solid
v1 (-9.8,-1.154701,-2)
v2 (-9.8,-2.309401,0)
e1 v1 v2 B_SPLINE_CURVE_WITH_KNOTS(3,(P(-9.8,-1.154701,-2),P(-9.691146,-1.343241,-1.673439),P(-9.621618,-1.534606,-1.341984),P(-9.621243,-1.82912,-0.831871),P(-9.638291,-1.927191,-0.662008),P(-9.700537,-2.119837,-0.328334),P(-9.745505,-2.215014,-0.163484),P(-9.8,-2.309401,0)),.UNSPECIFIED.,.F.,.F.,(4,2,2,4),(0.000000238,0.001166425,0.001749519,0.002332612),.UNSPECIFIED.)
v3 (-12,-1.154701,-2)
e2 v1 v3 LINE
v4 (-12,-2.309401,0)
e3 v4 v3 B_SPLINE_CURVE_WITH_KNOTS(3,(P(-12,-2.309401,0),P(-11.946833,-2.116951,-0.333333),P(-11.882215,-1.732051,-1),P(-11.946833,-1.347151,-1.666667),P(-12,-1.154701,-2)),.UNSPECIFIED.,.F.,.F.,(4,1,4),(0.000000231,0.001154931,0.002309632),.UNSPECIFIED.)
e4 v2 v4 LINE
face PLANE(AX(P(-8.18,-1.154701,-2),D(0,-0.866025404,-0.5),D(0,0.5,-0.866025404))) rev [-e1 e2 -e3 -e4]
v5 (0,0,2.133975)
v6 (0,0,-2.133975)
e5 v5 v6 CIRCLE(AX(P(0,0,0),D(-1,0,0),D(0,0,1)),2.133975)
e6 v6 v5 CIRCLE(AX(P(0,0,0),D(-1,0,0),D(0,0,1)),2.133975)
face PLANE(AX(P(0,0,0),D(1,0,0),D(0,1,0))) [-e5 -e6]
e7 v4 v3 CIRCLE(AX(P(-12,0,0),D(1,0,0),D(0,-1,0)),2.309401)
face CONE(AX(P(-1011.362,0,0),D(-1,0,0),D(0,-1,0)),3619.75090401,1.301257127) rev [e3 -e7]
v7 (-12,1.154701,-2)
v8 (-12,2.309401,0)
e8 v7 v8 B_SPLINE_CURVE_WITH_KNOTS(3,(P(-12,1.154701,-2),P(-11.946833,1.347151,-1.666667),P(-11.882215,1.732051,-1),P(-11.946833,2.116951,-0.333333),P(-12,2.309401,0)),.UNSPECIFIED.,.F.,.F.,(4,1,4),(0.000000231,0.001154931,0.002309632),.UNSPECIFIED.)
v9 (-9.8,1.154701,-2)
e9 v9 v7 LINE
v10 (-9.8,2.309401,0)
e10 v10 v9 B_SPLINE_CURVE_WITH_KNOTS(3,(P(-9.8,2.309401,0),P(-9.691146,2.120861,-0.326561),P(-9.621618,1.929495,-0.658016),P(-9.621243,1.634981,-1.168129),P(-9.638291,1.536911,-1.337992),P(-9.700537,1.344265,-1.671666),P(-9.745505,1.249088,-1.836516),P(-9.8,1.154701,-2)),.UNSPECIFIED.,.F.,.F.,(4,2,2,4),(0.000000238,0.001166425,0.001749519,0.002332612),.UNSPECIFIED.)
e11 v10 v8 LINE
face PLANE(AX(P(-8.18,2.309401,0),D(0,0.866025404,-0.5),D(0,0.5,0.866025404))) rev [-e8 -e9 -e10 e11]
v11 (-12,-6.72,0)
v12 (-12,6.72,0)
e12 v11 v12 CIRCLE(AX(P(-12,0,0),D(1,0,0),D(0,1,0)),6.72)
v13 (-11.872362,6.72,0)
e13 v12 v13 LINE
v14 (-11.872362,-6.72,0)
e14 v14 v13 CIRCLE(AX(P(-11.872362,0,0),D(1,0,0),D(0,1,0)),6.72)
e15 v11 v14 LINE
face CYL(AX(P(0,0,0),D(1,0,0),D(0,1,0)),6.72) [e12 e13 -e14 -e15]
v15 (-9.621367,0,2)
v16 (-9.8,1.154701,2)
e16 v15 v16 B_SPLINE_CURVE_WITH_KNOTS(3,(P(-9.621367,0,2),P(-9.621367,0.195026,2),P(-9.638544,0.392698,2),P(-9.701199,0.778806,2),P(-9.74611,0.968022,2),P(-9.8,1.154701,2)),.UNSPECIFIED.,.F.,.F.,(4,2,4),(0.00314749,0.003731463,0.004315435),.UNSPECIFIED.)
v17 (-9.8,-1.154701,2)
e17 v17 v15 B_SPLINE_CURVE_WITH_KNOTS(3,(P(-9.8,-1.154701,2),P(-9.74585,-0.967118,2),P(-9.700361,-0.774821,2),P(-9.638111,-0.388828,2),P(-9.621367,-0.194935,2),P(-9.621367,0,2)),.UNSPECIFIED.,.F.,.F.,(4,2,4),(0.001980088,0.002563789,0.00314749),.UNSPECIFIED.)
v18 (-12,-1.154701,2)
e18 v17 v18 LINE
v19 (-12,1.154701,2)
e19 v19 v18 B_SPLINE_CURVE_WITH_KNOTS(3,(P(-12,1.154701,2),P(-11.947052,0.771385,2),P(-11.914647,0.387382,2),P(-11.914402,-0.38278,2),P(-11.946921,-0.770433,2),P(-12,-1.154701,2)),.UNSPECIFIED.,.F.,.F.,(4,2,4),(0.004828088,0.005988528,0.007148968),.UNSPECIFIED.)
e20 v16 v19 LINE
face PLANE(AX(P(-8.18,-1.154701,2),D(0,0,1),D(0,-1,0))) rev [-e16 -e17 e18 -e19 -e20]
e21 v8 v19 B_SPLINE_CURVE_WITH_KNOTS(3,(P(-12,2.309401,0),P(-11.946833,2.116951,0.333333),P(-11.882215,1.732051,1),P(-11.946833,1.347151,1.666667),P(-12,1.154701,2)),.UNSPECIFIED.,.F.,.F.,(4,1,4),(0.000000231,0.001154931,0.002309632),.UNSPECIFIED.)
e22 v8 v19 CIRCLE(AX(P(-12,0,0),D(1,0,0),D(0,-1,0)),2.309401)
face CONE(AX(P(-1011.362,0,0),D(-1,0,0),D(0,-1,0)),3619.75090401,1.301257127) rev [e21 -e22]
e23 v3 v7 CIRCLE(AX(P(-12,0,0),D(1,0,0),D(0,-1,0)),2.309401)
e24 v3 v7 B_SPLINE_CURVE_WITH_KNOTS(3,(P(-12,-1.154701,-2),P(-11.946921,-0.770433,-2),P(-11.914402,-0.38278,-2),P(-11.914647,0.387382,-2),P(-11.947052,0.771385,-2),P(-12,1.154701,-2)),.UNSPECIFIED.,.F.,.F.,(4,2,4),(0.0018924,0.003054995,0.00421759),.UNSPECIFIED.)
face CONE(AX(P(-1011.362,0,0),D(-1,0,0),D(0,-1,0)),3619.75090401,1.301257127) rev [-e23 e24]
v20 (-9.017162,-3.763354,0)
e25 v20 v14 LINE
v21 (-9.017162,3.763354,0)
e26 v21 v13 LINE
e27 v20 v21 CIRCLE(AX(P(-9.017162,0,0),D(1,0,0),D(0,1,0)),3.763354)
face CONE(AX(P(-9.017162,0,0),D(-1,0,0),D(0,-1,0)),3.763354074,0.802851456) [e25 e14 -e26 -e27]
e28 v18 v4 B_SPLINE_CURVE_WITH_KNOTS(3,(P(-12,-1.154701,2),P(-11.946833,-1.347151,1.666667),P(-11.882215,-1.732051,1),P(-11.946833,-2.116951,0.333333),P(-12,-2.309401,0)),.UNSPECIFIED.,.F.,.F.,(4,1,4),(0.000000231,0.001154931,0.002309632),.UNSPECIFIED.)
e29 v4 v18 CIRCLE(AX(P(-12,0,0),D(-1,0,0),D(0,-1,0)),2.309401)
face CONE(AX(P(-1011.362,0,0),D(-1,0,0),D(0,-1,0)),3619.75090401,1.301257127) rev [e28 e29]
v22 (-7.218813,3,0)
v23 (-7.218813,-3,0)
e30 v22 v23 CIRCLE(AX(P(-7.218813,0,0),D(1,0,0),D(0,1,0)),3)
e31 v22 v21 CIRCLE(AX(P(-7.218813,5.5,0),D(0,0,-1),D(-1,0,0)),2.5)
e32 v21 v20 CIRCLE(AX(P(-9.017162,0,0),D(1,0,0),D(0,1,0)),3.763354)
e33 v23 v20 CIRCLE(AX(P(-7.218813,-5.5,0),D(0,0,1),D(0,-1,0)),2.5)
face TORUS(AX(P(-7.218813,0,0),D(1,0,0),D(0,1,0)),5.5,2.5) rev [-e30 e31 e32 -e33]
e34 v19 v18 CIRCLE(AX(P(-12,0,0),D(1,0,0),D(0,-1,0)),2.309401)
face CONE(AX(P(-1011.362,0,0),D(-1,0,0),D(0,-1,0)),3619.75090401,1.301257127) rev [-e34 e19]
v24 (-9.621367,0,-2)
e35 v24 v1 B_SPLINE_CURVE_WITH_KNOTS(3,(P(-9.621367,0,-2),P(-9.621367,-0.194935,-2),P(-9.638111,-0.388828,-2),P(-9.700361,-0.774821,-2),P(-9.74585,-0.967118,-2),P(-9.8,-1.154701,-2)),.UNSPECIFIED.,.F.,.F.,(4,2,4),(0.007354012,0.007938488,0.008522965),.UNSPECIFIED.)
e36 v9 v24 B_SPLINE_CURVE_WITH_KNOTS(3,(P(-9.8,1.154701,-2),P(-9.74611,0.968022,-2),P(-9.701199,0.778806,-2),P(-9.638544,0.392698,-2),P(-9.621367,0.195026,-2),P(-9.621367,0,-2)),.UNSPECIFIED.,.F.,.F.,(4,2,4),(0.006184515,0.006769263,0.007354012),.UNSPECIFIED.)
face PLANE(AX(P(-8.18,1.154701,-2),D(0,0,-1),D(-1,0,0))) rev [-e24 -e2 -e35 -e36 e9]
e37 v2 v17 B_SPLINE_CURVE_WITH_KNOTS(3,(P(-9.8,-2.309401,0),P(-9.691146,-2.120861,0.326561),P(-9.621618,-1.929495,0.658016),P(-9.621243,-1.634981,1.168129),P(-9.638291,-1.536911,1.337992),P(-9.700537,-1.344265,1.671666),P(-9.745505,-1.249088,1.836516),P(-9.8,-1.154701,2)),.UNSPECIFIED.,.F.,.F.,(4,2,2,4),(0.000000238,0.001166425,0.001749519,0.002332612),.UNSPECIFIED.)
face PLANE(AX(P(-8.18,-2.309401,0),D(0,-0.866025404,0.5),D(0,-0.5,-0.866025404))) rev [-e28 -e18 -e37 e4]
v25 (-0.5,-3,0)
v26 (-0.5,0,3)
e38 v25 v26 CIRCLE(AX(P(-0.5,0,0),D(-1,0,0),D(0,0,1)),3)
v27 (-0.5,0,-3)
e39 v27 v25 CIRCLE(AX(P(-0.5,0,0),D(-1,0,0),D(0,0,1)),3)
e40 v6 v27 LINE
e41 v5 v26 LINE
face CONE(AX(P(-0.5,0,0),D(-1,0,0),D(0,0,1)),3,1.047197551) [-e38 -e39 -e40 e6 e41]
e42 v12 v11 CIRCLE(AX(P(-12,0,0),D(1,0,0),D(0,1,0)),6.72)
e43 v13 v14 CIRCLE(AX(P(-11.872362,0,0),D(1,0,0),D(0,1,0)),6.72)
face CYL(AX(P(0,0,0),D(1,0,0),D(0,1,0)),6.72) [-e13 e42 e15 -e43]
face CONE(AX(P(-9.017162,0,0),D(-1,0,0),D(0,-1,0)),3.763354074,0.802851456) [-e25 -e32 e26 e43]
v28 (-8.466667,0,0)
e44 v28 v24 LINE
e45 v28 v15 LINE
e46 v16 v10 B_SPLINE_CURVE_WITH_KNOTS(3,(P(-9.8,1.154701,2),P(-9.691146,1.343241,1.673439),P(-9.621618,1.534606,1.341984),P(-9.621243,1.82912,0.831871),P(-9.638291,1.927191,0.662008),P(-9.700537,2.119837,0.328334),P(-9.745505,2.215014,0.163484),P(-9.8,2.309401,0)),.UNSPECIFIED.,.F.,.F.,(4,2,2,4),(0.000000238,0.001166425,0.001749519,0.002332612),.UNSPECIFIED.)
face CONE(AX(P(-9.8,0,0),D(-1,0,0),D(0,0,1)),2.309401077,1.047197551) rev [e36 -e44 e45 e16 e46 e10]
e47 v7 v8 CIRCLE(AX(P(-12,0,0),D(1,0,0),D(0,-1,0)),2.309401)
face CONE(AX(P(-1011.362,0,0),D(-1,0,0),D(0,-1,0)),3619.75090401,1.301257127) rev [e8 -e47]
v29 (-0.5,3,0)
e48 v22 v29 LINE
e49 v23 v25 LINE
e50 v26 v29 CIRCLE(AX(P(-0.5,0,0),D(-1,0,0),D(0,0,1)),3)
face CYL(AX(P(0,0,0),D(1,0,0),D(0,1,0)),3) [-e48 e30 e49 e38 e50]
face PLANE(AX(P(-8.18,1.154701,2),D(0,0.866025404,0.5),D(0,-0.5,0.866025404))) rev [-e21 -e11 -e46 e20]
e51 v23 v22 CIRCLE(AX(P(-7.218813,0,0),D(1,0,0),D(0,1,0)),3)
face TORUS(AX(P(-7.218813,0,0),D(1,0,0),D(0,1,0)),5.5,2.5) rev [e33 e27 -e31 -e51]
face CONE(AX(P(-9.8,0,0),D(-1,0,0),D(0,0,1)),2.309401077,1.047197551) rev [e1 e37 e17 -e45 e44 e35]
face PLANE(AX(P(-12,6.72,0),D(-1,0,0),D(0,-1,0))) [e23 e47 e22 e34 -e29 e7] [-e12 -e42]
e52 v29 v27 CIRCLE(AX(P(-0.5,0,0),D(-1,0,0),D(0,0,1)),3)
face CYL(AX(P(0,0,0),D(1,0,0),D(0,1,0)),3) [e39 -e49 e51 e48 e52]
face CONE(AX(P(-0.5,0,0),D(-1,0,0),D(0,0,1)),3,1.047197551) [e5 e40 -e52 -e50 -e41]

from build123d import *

# Parameters (mm, degrees)
CUT_EXTRUDE1_DEPTH = 3.82


with BuildPart() as part:
    # Sketch1 → Revolve1 (revolve)
    with BuildSketch(Plane.XY):
        with BuildLine():
            Line((0, 3), (-7.218812959, 3))
            ThreePointArc((-7.218812959, 3), (-8.195640781, 3.198737866), (-9.01716246, 3.763354074))
            Line((-9.01716246, 3.763354074), (-11.872362242, 6.72))
            Line((-11.872362242, 6.72), (-12, 6.72))
            Line((-12, 6.72), (-12, 0))
            Line((-12, 0), (0, 0))
            Line((0, 0), (0, 3))
        make_face()
    revolve(axis=Axis((0, 0, 0), (-1, 0, 0)))

    # Sketch2 → Cut-Extrude1 (cut)
    with BuildSketch(Plane.ZY.offset(12)):
        Polygon((0, 2.309401077), (-2, 1.154700538), (-2, -1.154700538), (0, -2.309401077), (2, -1.154700538), (2, 1.154700538), align=None)
    extrude(amount=-CUT_EXTRUDE1_DEPTH, mode=Mode.SUBTRACT)

    # Sketch6 → Revolve2 (revolve)
    with BuildSketch(Plane.XY, mode=Mode.PRIVATE) as revolve2_sk:
        Polygon((-9.8, 2.309401077), (-8.466666667, 0), (-7.6, 0), (-7.6, 2.309401077), align=None)
    revolve(revolve2_sk.sketch.rotate(Axis((-12, 0, 0), (1, 0, 0)), 90), axis=Axis((-12, 0, 0), (1, 0, 0)))

    # Sketch7 → Cut-Revolve2 (revolve, cut)
    with BuildSketch(Plane.XY, mode=Mode.PRIVATE) as cut_revolve2_sk:
        Polygon((-12, 2.309401077), (-12, 0), (-11.362, 0), align=None)
    revolve(cut_revolve2_sk.sketch.rotate(Axis((-12, 0, 0), (1, 0, 0)), 90), axis=Axis((-12, 0, 0), (1, 0, 0)), mode=Mode.SUBTRACT)

    # Sketch4 → Cut-Revolve1 (revolve, cut)
    with BuildSketch(Plane.XY, mode=Mode.PRIVATE) as cut_revolve1_sk:
        Polygon((-0.5, 3), (0, 2.133974596), (0.5, 3), align=None)
    revolve(cut_revolve1_sk.sketch.rotate(Axis((-0.5, 0, 0), (1, 0, 0)), 90), axis=Axis((-0.5, 0, 0), (1, 0, 0)), mode=Mode.SUBTRACT)


solid = part.part
